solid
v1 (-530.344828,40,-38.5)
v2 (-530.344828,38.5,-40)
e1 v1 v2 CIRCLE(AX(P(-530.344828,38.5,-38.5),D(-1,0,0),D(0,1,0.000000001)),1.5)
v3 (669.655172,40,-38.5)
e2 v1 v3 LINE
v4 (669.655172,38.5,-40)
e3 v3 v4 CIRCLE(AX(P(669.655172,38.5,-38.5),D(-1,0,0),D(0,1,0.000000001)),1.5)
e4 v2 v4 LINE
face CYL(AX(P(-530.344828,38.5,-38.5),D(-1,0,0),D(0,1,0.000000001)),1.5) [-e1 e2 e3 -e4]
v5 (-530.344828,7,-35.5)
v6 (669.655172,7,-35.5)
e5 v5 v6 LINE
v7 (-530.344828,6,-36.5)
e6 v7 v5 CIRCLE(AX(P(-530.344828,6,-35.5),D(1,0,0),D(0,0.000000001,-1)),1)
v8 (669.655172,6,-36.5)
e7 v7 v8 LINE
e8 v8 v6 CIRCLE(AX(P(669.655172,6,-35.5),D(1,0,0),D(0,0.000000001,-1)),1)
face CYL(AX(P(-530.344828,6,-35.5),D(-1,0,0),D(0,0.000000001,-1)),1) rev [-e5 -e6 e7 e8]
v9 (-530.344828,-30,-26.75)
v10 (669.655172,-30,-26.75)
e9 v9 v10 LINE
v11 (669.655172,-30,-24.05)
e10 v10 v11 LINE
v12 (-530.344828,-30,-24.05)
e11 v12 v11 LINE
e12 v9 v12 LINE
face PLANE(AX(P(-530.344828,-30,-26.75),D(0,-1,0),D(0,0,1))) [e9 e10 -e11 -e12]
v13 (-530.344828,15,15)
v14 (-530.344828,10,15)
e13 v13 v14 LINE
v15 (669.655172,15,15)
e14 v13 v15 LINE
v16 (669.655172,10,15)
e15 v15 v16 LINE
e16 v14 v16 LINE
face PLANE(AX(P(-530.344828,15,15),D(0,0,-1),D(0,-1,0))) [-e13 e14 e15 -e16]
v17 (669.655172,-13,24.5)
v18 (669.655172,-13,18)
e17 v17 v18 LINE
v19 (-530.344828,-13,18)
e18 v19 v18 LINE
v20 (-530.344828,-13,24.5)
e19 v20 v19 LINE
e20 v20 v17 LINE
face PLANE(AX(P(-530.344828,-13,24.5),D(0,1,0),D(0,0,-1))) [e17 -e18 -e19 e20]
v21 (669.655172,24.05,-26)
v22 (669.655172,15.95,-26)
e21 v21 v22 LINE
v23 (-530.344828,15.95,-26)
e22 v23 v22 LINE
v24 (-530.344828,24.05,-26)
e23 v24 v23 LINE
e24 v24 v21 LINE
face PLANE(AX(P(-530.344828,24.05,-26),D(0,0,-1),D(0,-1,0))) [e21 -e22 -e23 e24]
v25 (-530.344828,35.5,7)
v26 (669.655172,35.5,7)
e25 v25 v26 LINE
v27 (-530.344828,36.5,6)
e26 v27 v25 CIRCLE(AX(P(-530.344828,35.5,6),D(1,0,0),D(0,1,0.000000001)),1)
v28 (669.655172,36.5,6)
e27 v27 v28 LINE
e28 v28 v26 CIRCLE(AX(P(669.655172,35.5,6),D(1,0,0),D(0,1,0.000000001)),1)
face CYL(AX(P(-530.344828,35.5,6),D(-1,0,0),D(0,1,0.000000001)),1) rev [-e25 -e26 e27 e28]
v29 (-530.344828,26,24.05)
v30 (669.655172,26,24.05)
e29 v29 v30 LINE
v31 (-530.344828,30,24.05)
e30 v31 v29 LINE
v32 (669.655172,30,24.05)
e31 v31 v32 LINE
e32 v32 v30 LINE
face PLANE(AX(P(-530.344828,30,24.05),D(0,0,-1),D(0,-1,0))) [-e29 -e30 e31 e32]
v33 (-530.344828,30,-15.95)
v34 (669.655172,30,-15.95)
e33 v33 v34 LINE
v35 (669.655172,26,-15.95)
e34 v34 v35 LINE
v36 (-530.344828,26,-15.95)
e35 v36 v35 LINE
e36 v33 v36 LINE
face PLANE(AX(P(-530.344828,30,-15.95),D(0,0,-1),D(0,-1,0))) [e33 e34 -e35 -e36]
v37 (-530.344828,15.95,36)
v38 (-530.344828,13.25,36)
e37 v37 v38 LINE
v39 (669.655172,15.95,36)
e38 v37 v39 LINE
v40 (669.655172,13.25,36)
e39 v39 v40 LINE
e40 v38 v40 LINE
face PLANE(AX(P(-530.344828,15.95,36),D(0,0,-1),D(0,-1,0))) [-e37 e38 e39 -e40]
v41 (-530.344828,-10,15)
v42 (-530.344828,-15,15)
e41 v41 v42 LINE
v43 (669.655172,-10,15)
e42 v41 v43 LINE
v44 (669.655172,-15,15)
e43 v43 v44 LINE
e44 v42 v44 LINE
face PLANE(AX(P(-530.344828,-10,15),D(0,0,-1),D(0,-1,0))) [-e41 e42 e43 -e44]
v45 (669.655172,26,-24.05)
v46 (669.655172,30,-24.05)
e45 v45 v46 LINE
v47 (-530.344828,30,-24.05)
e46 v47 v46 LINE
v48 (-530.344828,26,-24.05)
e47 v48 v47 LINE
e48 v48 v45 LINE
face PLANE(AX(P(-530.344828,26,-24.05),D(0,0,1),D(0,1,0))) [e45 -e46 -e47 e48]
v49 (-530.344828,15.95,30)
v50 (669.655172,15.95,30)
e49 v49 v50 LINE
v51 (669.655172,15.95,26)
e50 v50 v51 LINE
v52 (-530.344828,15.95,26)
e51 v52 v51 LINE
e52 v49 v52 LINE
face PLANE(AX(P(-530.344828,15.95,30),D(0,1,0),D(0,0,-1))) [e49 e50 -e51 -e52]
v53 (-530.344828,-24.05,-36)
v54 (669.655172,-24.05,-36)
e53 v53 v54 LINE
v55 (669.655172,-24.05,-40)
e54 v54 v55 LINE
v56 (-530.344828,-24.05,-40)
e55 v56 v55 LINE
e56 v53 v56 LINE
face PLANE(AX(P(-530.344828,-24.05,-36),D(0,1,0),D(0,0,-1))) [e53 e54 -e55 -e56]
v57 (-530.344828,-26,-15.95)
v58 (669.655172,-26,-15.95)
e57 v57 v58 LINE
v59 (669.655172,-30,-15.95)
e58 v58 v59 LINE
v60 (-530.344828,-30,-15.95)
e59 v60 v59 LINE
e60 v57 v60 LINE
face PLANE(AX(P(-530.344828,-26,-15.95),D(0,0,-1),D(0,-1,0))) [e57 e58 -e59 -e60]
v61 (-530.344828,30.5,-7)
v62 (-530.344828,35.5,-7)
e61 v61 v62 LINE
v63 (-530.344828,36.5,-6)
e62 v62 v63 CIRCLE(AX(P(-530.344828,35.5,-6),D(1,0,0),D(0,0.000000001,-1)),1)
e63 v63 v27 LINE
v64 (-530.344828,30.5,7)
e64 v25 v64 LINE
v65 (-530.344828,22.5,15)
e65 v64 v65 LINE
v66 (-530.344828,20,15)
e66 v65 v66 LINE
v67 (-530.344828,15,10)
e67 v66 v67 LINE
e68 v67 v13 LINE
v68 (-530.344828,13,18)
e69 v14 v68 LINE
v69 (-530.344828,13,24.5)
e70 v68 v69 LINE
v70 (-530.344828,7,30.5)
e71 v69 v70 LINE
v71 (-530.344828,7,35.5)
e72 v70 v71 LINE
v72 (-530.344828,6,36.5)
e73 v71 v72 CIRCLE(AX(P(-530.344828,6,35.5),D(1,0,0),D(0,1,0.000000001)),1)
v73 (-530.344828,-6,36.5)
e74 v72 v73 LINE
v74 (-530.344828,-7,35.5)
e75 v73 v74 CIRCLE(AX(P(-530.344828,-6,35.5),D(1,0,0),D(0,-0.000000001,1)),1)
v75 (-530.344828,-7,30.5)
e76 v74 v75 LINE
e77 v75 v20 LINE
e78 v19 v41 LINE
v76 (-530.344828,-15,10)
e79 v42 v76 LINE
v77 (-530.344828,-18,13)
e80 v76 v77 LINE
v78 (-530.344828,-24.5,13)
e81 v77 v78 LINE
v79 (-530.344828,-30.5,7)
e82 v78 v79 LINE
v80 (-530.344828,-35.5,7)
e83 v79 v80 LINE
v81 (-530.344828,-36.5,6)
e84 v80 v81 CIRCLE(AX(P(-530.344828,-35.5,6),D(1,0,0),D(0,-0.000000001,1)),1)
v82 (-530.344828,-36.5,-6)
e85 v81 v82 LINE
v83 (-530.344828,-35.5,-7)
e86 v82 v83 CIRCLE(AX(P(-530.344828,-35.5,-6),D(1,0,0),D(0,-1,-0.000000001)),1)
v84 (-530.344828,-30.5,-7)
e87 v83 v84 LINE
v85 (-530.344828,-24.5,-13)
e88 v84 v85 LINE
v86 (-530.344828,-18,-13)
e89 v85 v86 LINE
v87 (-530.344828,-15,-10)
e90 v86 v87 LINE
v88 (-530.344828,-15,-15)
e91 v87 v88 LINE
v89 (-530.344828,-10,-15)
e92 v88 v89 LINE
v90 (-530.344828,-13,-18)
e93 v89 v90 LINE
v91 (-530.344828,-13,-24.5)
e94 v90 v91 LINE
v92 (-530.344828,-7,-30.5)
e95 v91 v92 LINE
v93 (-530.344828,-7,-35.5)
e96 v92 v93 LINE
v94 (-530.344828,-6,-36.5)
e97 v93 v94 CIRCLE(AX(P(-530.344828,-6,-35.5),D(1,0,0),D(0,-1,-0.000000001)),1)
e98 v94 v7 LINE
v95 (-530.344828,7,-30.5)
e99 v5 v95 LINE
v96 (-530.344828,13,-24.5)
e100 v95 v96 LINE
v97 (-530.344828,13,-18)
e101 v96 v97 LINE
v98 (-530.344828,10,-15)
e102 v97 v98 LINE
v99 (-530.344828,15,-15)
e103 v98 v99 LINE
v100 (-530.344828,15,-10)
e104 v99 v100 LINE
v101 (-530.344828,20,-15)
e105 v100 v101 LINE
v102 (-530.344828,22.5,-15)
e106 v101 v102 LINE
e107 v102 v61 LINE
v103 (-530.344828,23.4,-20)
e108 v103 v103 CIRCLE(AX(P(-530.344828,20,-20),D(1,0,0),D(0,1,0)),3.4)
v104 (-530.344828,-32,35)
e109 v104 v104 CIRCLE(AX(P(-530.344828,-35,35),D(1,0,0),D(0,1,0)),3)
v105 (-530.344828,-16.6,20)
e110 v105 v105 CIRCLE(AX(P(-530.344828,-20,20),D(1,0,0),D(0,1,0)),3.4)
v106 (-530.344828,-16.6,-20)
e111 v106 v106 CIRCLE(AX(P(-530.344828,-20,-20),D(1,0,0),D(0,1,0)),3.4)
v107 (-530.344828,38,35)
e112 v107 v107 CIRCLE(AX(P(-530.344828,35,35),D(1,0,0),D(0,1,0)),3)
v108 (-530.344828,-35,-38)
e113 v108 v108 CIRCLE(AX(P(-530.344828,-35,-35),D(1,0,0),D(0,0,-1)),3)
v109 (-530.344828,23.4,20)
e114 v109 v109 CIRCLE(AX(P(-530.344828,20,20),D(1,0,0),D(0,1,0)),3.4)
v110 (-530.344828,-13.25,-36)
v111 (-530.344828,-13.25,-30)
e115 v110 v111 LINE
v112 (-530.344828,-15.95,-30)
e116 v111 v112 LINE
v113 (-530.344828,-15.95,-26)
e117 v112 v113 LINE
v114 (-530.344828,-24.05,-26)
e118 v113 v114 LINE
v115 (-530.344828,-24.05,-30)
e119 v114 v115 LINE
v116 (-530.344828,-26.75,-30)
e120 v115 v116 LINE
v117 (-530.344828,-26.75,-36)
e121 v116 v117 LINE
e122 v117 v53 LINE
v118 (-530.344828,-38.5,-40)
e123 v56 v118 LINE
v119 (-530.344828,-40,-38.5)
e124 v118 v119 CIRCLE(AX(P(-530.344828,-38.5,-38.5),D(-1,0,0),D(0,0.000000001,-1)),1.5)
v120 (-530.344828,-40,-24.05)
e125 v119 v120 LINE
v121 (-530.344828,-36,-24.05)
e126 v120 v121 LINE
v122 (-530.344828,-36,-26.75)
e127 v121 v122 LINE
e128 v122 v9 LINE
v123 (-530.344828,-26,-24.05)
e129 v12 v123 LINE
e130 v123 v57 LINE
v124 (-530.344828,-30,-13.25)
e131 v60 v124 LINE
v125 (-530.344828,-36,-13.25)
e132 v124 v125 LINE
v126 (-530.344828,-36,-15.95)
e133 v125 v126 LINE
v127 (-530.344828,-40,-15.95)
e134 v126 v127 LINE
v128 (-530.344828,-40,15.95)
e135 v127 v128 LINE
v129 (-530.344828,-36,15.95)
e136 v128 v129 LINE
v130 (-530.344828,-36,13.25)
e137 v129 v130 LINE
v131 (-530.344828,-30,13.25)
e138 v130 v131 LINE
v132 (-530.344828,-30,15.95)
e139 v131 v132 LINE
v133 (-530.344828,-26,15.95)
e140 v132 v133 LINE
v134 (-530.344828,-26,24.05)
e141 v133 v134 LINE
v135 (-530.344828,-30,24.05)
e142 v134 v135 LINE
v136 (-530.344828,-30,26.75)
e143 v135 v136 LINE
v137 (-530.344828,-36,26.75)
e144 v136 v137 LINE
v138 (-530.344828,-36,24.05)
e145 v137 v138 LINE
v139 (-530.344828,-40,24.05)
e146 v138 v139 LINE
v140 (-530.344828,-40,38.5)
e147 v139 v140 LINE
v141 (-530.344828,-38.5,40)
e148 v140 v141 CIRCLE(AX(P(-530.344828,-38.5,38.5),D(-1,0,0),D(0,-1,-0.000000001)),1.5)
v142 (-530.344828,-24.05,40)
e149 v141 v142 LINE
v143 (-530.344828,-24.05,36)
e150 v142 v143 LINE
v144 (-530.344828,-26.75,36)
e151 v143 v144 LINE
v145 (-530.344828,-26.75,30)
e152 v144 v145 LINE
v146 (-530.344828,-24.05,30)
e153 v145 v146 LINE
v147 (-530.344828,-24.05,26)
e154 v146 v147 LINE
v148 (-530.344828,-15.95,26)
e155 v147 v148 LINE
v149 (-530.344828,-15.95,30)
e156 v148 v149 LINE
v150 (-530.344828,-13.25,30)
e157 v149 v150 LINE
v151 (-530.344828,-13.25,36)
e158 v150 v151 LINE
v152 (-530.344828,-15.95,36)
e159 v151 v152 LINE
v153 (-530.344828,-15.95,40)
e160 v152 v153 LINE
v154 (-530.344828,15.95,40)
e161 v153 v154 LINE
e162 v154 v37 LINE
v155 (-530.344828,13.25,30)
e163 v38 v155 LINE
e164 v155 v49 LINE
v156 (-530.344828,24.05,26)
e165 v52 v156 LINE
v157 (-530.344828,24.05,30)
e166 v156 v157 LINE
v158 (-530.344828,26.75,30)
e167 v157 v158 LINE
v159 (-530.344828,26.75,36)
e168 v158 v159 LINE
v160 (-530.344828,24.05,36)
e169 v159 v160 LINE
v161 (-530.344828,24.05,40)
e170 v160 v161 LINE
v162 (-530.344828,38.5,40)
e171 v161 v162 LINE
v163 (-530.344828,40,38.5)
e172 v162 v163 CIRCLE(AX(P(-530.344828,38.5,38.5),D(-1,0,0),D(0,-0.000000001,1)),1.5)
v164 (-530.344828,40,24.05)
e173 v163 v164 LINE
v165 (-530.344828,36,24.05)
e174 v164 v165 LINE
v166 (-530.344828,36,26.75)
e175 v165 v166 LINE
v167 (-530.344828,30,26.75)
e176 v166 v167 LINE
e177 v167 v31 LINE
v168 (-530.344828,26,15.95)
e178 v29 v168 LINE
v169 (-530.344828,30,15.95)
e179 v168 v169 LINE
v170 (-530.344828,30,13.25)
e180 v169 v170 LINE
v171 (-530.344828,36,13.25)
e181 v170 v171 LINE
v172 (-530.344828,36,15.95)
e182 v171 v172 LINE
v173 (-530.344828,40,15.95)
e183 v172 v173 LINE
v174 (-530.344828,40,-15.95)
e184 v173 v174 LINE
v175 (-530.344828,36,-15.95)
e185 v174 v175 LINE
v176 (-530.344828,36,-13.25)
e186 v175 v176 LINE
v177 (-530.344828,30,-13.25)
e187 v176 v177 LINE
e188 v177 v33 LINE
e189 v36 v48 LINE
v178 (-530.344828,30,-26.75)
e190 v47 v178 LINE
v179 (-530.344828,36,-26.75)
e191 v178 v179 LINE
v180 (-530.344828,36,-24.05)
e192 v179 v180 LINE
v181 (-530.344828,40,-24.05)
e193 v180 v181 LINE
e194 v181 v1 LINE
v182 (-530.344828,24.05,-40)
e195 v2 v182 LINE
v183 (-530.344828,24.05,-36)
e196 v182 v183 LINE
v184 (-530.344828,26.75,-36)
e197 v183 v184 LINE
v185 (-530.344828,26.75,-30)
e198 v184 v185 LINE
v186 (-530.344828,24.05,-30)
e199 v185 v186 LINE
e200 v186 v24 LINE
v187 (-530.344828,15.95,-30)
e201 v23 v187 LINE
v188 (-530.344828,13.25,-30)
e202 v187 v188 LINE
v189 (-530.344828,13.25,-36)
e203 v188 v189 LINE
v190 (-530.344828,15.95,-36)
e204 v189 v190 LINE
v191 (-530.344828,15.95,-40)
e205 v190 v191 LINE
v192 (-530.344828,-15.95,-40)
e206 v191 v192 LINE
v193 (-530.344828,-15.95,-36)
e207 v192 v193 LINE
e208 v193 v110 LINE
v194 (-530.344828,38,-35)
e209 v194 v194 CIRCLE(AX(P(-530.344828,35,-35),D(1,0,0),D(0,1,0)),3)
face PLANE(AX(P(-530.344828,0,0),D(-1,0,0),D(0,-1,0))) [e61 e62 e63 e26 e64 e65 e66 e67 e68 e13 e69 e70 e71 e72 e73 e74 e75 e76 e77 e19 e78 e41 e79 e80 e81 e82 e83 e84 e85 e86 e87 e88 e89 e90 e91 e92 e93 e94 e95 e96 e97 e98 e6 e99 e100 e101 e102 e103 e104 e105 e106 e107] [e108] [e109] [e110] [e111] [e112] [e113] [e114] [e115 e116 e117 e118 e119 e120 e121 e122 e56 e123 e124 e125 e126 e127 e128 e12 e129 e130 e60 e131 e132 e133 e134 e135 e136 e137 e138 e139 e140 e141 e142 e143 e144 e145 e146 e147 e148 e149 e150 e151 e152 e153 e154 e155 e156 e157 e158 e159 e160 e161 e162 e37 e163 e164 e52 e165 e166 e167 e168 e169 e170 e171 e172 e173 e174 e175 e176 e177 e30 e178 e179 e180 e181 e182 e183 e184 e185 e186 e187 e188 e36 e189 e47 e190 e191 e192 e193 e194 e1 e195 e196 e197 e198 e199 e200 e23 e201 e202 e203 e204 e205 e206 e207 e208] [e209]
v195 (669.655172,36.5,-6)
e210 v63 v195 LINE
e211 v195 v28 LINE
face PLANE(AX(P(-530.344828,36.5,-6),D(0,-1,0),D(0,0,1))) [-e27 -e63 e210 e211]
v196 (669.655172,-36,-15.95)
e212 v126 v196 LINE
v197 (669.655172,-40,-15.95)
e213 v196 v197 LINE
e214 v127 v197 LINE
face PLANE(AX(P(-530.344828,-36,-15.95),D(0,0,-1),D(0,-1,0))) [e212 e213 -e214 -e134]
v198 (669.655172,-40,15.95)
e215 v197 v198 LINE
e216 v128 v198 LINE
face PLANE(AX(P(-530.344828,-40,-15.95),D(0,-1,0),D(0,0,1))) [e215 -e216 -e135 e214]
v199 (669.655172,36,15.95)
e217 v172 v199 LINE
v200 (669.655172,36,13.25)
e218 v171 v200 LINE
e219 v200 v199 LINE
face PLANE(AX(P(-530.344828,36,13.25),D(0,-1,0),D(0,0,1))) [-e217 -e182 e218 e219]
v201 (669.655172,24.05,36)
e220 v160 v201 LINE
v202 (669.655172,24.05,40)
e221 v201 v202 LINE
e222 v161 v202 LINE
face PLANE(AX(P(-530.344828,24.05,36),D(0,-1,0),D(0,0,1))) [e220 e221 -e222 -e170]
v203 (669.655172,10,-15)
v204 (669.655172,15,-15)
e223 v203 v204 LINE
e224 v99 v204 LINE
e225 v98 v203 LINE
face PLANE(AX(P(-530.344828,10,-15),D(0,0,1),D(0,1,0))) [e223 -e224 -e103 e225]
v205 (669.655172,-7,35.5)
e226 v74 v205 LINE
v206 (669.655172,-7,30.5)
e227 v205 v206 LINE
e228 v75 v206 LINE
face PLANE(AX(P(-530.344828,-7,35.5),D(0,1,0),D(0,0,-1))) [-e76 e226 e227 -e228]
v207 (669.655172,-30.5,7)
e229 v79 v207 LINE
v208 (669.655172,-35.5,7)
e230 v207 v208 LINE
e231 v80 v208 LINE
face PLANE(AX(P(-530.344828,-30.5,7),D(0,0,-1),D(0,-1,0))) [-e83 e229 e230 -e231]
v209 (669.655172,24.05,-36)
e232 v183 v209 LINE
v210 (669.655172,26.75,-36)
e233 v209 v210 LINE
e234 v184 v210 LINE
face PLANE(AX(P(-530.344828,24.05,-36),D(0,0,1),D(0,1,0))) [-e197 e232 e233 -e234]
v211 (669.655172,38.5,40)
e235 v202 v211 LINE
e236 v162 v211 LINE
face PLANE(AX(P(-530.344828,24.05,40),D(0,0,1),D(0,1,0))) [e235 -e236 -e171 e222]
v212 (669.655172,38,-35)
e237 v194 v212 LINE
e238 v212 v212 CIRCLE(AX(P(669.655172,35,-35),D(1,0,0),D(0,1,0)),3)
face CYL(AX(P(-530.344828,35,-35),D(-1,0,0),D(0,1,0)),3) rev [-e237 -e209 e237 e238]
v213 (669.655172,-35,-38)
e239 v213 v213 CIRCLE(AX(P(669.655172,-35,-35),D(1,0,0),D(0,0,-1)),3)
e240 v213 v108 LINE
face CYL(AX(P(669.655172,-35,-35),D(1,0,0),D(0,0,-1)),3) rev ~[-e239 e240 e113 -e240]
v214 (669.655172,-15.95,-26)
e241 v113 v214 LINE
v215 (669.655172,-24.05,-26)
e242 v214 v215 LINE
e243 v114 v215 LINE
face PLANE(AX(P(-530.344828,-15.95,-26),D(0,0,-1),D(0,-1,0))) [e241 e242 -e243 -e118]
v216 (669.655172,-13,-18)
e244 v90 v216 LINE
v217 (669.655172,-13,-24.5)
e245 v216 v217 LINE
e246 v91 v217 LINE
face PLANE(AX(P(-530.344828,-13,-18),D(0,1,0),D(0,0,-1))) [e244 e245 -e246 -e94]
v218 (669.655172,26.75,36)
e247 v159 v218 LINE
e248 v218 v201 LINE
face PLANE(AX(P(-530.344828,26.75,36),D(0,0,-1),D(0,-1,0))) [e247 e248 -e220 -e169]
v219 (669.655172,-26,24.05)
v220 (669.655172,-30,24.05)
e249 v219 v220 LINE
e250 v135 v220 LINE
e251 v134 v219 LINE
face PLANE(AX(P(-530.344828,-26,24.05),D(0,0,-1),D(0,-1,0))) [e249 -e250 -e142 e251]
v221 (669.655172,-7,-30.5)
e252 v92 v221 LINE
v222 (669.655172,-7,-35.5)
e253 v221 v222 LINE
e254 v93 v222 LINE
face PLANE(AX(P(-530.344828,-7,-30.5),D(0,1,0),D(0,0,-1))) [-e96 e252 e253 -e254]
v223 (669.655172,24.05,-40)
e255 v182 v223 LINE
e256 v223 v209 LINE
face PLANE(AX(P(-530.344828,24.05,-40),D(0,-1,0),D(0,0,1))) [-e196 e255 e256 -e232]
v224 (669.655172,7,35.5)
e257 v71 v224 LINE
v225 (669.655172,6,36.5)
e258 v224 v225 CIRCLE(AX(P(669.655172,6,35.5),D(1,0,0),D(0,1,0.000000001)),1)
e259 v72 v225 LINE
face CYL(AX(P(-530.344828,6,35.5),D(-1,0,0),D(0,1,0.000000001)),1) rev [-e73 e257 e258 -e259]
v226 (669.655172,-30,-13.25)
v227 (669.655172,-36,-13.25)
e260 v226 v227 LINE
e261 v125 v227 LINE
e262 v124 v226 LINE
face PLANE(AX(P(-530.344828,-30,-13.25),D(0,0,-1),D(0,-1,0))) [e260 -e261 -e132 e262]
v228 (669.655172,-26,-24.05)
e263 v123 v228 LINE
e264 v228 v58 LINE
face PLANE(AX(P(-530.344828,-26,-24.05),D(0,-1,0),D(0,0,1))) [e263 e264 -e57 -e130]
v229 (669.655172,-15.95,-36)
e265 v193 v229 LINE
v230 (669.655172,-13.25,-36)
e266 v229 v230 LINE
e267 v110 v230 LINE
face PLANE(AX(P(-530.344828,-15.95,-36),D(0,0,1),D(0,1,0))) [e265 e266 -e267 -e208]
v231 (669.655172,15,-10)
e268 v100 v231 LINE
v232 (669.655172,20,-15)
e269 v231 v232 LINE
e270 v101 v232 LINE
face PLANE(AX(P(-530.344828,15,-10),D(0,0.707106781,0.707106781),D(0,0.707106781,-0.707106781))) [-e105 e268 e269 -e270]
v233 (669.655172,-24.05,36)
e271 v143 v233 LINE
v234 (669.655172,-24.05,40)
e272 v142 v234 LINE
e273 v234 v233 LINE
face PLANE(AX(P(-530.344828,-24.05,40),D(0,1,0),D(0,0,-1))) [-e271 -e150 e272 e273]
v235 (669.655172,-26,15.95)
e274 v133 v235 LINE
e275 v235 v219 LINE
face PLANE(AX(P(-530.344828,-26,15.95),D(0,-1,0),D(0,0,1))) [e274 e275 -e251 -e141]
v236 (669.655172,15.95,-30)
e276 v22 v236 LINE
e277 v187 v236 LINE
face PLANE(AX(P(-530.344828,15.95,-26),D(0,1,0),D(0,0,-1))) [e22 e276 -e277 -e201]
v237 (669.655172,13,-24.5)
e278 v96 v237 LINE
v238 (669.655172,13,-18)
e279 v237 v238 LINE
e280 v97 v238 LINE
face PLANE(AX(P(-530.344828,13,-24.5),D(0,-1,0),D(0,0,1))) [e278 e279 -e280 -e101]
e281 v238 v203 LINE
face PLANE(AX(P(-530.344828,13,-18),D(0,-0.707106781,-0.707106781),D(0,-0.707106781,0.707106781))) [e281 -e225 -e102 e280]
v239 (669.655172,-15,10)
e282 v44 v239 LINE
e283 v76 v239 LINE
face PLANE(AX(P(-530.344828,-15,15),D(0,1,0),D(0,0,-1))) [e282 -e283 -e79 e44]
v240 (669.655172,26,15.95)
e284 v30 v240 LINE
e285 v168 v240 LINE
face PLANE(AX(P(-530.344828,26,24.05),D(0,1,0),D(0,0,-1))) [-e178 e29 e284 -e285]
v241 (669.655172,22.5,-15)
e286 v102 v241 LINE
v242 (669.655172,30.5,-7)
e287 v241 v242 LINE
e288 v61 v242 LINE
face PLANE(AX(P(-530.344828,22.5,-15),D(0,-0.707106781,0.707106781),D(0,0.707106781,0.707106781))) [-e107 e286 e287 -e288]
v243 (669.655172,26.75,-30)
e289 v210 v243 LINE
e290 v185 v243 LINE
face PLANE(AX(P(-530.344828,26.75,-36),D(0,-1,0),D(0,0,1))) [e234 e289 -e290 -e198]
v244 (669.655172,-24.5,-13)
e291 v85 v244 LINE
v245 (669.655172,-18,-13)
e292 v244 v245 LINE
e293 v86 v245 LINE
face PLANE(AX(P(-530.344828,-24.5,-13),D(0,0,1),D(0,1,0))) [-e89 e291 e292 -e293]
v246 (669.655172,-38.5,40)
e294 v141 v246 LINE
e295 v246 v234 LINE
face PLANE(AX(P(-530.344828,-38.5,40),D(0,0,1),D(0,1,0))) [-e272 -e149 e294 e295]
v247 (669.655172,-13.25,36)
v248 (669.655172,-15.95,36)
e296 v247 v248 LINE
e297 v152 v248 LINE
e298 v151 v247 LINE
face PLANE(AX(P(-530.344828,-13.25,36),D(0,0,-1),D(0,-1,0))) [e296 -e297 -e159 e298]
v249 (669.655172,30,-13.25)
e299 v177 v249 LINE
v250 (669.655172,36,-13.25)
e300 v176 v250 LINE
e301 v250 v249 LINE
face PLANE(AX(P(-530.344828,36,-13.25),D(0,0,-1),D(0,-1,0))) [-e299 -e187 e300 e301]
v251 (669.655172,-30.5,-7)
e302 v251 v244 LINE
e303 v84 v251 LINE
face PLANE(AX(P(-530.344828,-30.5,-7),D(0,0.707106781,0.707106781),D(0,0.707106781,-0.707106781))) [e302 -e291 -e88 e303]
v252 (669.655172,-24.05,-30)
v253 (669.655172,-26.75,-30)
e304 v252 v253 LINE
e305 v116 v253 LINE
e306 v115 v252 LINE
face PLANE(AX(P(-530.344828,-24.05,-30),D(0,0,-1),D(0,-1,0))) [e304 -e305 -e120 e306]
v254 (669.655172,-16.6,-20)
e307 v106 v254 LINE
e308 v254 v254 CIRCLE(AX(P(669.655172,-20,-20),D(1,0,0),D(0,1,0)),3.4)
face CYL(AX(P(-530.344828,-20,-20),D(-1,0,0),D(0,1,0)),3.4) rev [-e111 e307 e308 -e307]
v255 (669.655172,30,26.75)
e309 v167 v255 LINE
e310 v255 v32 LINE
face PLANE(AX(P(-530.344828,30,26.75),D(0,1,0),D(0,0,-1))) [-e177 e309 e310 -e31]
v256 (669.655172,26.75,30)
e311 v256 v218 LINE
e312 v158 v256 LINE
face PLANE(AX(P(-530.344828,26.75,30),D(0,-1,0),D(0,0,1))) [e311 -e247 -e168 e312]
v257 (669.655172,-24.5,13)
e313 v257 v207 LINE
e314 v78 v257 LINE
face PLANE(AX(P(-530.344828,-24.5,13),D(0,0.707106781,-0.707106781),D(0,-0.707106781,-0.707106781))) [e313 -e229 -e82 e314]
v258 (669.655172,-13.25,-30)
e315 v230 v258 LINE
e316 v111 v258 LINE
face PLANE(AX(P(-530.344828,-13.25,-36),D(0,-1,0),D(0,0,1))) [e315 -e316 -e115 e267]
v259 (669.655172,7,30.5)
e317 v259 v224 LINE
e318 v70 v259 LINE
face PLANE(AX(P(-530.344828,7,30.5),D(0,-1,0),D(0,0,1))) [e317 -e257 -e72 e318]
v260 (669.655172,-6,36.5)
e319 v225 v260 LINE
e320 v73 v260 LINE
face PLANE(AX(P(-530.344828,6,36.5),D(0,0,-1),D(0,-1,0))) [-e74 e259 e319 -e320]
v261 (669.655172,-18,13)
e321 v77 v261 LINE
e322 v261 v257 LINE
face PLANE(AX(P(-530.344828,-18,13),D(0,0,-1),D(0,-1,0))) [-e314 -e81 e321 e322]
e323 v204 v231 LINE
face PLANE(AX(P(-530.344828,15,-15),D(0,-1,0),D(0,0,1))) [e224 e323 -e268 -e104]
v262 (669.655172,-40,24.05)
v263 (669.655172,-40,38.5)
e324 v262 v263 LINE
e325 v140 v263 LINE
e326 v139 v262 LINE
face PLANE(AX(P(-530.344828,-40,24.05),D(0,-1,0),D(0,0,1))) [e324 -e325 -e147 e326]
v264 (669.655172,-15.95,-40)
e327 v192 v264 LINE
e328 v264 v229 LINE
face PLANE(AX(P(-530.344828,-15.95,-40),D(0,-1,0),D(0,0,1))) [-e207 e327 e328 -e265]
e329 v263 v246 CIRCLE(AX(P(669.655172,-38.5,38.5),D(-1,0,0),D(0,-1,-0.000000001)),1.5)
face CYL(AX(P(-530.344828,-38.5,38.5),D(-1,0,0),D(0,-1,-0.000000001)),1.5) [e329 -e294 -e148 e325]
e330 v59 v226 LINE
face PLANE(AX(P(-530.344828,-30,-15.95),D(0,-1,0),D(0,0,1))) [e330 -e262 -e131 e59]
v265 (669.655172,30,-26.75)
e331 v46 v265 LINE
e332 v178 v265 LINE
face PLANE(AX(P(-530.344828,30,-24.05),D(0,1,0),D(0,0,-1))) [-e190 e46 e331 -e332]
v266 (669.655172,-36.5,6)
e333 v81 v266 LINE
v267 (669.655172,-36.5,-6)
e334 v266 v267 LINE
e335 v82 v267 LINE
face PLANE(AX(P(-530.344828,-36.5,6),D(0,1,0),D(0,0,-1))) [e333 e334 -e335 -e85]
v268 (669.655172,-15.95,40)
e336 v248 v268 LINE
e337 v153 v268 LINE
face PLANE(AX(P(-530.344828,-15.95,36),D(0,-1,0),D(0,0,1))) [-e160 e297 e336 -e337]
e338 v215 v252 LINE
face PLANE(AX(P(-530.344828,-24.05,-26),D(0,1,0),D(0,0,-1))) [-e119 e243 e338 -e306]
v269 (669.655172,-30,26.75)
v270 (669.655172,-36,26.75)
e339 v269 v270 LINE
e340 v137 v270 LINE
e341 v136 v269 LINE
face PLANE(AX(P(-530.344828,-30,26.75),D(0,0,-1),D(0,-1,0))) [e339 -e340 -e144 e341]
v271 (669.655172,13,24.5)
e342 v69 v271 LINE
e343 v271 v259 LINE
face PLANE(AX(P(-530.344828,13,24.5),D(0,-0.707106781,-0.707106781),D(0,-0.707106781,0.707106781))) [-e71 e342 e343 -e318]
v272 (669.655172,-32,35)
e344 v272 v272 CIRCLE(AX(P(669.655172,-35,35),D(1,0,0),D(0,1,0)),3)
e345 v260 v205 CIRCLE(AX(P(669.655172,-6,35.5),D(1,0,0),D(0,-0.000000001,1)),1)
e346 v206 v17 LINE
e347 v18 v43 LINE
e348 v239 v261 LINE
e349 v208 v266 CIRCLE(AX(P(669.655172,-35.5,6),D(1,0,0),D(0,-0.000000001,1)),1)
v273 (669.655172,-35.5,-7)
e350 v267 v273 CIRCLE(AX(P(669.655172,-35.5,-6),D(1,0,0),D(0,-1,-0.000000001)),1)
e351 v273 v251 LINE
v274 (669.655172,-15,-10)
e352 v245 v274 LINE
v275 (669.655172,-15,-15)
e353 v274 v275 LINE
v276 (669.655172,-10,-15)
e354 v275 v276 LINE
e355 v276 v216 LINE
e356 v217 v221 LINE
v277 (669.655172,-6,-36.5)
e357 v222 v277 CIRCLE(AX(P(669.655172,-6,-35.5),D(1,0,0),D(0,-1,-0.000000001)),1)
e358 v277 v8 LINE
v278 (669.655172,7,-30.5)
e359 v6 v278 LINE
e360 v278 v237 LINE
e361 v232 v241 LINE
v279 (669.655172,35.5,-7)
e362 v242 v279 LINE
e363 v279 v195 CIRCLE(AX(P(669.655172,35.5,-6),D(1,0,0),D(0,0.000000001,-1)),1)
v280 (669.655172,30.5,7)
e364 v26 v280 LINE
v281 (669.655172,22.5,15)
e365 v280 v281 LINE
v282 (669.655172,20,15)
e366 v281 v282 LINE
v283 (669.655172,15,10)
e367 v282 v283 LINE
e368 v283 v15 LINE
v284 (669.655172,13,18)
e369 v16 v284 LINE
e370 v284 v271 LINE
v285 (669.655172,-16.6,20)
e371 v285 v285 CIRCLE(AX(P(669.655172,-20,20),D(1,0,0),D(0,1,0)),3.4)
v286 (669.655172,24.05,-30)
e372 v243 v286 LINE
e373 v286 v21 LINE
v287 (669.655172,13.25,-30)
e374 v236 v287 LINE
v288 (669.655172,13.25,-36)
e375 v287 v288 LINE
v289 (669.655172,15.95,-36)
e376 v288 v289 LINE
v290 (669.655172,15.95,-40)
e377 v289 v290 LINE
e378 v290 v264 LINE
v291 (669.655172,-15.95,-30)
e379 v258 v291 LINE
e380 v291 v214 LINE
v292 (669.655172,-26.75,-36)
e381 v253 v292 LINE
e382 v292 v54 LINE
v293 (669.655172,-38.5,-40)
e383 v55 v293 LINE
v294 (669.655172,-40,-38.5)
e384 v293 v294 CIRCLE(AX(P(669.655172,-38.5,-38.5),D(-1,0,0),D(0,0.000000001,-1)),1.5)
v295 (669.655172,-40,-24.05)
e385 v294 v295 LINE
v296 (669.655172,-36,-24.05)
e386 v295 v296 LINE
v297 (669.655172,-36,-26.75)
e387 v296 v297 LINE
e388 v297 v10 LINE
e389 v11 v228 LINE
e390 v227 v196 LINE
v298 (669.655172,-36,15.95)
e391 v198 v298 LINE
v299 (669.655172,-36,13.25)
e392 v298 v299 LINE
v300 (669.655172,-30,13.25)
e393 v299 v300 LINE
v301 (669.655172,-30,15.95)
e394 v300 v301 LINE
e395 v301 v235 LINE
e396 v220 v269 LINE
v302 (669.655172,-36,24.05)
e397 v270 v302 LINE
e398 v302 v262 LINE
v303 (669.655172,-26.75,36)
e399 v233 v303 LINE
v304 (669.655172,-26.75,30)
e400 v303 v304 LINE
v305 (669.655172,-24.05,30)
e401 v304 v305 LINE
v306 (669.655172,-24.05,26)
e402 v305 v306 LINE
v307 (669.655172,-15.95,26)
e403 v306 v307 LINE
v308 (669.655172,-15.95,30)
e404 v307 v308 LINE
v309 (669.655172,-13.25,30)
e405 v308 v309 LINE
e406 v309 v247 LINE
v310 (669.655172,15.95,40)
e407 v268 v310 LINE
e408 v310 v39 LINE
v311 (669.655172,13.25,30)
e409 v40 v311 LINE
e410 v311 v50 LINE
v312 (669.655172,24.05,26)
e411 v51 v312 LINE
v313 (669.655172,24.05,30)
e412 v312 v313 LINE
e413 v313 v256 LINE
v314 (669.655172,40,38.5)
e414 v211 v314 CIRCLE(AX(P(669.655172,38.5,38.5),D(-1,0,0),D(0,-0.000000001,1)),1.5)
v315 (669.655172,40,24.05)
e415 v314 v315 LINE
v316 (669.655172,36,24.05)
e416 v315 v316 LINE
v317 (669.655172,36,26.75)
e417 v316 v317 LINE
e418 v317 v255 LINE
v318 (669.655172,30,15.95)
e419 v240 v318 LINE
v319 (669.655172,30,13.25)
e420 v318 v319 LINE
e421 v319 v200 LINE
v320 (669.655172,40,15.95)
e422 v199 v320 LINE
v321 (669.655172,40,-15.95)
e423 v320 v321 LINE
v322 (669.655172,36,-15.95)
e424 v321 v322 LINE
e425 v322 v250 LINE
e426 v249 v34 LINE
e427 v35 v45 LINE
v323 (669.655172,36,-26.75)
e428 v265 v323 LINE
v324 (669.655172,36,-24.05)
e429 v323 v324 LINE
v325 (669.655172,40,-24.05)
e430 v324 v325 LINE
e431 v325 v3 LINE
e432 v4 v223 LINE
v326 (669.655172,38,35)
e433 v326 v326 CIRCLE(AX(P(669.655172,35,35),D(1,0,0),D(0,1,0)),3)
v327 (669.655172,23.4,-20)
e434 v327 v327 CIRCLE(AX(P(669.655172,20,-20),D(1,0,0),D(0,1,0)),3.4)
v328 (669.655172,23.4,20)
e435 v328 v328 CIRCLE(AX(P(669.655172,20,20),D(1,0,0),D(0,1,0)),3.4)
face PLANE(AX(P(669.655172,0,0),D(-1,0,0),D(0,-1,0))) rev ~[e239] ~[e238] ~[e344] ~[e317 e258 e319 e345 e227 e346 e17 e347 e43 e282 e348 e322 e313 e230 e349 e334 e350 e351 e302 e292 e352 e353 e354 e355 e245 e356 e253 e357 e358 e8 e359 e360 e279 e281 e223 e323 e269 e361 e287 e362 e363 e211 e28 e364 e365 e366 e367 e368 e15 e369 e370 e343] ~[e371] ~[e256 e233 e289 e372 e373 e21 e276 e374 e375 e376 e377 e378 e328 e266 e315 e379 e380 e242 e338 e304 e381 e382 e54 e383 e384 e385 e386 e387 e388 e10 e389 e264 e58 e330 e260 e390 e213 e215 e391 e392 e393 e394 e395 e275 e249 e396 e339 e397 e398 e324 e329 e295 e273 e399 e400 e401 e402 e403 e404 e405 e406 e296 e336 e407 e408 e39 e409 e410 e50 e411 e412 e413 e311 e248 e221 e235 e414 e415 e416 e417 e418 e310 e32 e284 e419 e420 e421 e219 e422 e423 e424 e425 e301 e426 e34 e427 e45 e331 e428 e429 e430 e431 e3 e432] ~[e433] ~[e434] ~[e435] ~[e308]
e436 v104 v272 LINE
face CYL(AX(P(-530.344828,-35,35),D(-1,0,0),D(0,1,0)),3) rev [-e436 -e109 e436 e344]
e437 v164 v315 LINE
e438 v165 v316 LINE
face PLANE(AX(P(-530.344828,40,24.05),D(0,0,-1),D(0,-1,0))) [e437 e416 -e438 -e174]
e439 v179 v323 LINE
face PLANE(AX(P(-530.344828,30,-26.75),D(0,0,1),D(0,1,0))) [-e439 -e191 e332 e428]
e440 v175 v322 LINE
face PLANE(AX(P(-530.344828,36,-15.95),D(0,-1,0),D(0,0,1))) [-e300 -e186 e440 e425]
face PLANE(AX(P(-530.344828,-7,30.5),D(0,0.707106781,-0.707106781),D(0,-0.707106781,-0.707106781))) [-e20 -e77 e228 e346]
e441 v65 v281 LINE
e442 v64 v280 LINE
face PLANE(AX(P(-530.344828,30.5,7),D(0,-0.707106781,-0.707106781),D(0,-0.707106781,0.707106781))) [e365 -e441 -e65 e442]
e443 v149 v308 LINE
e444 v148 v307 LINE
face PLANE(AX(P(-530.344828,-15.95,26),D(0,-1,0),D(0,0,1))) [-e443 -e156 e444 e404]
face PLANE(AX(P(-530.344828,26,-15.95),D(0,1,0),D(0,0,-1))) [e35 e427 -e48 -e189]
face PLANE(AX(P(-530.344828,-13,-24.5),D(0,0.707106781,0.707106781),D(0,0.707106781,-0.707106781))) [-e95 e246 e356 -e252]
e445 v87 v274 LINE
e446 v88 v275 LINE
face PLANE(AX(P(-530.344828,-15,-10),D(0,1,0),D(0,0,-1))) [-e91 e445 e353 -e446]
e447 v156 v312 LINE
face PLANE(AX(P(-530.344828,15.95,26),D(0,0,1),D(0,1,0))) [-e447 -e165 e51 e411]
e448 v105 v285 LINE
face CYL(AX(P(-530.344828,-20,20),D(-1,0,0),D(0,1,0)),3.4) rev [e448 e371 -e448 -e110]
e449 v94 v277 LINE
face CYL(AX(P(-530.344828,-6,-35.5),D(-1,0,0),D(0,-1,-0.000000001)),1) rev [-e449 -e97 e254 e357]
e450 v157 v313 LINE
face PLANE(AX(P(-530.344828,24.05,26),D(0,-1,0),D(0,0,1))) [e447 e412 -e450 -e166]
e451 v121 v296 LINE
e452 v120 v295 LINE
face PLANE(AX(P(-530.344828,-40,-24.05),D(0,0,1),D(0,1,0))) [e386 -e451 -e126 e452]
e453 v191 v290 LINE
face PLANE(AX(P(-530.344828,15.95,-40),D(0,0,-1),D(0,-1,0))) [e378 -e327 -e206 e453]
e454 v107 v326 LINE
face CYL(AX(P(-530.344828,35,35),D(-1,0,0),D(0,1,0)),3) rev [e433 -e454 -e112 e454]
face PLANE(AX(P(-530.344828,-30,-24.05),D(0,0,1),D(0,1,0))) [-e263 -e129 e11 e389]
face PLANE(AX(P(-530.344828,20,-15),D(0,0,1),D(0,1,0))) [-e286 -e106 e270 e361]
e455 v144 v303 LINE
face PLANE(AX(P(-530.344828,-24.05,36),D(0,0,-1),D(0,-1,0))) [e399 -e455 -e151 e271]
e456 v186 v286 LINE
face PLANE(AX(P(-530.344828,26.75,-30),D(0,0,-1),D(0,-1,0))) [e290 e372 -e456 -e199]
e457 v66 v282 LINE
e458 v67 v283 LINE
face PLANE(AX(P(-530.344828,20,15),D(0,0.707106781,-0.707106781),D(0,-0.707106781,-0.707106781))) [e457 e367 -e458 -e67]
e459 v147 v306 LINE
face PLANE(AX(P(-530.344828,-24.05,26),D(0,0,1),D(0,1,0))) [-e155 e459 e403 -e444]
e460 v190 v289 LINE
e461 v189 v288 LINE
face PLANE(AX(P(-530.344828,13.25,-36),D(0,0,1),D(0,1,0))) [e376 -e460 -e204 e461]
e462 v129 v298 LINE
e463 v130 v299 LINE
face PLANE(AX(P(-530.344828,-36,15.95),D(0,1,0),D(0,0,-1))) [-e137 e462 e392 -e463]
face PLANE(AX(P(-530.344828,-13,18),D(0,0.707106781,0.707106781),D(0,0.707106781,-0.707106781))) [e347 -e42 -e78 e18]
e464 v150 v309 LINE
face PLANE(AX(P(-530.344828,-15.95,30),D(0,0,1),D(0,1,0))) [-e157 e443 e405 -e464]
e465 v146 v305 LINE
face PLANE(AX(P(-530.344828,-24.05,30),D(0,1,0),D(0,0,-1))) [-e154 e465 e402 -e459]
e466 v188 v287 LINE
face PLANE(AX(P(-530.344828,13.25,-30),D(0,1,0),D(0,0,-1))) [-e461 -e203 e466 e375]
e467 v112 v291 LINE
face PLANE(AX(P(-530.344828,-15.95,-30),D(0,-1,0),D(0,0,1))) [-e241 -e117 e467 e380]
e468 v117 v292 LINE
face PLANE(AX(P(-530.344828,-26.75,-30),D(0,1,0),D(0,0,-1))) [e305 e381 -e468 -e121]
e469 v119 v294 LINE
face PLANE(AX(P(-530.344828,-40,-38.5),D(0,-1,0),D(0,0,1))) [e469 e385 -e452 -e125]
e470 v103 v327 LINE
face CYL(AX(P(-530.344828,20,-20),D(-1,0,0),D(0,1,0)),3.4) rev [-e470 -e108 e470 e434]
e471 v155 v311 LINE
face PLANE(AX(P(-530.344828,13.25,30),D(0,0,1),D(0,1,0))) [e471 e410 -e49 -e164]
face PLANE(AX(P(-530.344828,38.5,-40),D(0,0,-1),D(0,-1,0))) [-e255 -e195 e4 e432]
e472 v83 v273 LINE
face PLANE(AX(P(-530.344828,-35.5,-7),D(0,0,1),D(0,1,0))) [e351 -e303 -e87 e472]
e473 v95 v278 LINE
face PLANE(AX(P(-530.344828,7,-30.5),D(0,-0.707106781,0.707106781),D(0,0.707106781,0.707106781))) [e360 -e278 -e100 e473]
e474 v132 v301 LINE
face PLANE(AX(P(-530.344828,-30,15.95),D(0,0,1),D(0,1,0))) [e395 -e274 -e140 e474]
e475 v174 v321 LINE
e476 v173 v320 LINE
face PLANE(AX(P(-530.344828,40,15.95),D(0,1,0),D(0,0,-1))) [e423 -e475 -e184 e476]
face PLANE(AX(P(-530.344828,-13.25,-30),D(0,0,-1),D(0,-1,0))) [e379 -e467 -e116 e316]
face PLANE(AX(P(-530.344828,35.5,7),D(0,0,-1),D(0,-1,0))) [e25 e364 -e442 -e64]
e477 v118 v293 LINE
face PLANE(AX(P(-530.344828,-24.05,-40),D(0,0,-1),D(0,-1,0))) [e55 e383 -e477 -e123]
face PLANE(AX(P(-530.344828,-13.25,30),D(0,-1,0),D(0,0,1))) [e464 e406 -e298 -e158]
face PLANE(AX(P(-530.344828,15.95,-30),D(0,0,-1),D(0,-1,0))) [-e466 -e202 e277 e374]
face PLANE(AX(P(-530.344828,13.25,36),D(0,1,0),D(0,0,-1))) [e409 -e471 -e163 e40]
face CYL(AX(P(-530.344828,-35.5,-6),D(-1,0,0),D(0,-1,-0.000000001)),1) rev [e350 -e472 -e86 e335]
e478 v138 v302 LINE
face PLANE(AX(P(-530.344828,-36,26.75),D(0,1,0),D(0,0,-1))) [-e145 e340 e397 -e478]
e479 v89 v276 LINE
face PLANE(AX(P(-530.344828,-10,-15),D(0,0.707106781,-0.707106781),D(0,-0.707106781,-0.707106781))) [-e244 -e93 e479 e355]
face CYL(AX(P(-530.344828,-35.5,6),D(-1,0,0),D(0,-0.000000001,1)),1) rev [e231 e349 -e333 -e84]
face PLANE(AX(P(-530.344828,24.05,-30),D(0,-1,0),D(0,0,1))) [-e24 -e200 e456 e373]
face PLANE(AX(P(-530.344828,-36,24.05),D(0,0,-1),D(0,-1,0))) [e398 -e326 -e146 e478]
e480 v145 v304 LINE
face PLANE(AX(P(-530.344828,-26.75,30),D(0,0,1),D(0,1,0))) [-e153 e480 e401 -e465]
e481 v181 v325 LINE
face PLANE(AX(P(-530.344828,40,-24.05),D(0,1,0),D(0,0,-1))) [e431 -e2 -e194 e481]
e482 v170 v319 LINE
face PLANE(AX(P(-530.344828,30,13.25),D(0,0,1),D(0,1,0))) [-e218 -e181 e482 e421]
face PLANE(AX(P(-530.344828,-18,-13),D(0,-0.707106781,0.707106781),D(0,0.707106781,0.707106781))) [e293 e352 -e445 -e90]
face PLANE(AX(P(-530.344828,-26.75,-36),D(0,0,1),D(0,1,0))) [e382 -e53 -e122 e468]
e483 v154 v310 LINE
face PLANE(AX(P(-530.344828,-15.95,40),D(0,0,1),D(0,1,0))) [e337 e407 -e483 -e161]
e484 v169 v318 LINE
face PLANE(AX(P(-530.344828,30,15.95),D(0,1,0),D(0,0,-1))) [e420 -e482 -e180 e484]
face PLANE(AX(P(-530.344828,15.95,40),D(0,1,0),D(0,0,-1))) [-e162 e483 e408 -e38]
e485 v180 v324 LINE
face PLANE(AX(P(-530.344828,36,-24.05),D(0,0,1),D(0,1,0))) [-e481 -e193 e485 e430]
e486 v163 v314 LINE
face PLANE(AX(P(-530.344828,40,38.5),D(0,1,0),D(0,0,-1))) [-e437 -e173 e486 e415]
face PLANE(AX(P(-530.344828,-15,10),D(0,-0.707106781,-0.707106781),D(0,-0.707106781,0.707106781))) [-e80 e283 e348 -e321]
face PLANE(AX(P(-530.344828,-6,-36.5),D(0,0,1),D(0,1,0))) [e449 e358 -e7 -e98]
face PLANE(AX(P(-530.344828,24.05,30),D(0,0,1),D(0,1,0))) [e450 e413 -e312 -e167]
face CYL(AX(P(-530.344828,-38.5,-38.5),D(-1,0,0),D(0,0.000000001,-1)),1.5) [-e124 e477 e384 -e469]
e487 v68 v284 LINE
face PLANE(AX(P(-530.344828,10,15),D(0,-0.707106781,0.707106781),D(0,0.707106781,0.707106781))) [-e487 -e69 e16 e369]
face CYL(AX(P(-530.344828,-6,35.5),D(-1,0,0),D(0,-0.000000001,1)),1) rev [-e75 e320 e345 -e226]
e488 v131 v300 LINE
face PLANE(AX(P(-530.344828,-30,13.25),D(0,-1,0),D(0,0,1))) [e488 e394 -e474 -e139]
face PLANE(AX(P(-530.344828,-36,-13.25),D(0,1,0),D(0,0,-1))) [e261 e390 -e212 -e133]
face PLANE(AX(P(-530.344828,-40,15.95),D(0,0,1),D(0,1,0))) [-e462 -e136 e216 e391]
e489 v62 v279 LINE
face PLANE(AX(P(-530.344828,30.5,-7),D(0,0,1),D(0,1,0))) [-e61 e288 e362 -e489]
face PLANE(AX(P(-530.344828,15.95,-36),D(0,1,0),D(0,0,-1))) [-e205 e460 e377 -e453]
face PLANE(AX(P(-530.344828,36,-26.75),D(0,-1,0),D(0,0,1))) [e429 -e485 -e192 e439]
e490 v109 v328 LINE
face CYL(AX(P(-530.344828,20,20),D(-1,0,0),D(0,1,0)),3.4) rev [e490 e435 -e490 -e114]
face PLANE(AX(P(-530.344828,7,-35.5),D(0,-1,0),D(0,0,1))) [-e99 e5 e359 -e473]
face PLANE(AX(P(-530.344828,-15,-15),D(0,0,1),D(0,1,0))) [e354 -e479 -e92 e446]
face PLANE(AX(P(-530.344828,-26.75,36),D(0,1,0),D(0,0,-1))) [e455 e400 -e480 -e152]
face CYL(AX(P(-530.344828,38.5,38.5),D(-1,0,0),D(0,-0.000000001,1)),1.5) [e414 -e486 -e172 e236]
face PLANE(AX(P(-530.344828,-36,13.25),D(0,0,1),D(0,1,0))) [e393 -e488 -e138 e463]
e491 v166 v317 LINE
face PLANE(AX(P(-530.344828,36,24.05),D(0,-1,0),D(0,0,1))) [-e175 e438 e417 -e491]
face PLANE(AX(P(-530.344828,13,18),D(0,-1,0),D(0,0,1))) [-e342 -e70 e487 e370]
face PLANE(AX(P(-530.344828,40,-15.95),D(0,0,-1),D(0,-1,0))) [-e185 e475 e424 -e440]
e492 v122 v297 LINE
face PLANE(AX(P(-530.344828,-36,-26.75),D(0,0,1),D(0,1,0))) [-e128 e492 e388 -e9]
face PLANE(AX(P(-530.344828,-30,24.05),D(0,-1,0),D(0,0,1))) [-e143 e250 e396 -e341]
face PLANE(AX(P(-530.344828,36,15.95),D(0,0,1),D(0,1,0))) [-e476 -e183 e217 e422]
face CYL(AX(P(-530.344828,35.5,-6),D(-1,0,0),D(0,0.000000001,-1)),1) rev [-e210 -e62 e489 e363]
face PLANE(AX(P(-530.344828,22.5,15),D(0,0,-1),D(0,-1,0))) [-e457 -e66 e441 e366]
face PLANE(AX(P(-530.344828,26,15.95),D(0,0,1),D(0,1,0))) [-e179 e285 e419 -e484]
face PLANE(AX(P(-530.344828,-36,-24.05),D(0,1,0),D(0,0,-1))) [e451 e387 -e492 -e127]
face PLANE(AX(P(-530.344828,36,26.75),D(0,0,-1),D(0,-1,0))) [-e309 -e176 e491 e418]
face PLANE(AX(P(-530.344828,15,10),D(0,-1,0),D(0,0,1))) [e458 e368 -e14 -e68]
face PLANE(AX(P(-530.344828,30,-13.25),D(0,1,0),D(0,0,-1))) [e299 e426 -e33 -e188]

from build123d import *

# Parameters (mm, degrees)
SKETCH1_R                                 = 3.4
SKETCH1_R_2                               = 3
ALUMINIUM_PROFILE_80_X_80G_X_R1_5_1_DEPTH = 1200
SKETCH10_R                                = 3
CUT_EXTRUDE1_DEPTH                        = 1202.332593414


with BuildPart() as part:
    # Sketch1 → Aluminium profile 80 X 80G X R1.5(1) (new body)
    with BuildSketch(Plane.YZ.offset(-530.344827586)):
        with BuildLine():
            Line((-24.05, 40), (-24.05, 36))
            Line((-24.05, 36), (-26.75, 36))
            Line((-26.75, 36), (-26.75, 30))
            Line((-26.75, 30), (-24.05, 30))
            Line((-24.05, 30), (-24.05, 26))
            Line((-24.05, 26), (-15.95, 26))
            Line((-15.95, 26), (-15.95, 30))
            Line((-15.95, 30), (-13.25, 30))
            Line((-13.25, 30), (-13.25, 36))
            Line((-13.25, 36), (-15.95, 36))
            Line((-15.95, 36), (-15.95, 40))
            Line((-15.95, 40), (15.95, 40))
            Line((15.95, 40), (15.95, 36))
            Line((15.95, 36), (13.25, 36))
            Line((13.25, 36), (13.25, 30))
            Line((13.25, 30), (15.95, 30))
            Line((15.95, 30), (15.95, 26))
            Line((15.95, 26), (24.05, 26))
            Line((24.05, 26), (24.05, 30))
            Line((24.05, 30), (26.75, 30))
            Line((26.75, 30), (26.75, 36))
            Line((26.75, 36), (24.05, 36))
            Line((24.05, 36), (24.05, 40))
            Line((24.05, 40), (38.5, 40))
            ThreePointArc((38.5, 40), (39.560660172, 39.560660172), (40, 38.5))
            Line((40, 38.5), (40, 24.05))
            Line((40, 24.05), (36, 24.05))
            Line((36, 24.05), (36, 26.75))
            Line((36, 26.75), (30, 26.75))
            Line((30, 26.75), (30, 24.05))
            Line((30, 24.05), (26, 24.05))
            Line((26, 24.05), (26, 15.95))
            Line((26, 15.95), (30, 15.95))
            Line((30, 15.95), (30, 13.25))
            Line((30, 13.25), (36, 13.25))
            Line((36, 13.25), (36, 15.95))
            Line((36, 15.95), (40, 15.95))
            Line((40, 15.95), (40, -15.95))
            Line((40, -15.95), (36, -15.95))
            Line((36, -15.95), (36, -13.25))
            Line((36, -13.25), (30, -13.25))
            Line((30, -13.25), (30, -15.95))
            Line((30, -15.95), (26, -15.95))
            Line((26, -15.95), (26, -24.05))
            Line((26, -24.05), (30, -24.05))
            Line((30, -24.05), (30, -26.75))
            Line((30, -26.75), (36, -26.75))
            Line((36, -26.75), (36, -24.05))
            Line((36, -24.05), (40, -24.05))
            Line((40, -24.05), (40, -38.5))
            ThreePointArc((40, -38.5), (39.560660172, -39.560660172), (38.5, -40))
            Line((38.5, -40), (24.05, -40))
            Line((24.05, -40), (24.05, -36))
            Line((24.05, -36), (26.75, -36))
            Line((26.75, -36), (26.75, -30))
            Line((26.75, -30), (24.05, -30))
            Line((24.05, -30), (24.05, -26))
            Line((24.05, -26), (15.95, -26))
            Line((15.95, -26), (15.95, -30))
            Line((15.95, -30), (13.25, -30))
            Line((13.25, -30), (13.25, -36))
            Line((13.25, -36), (15.95, -36))
            Line((15.95, -36), (15.95, -40))
            Line((15.95, -40), (-15.95, -40))
            Line((-15.95, -40), (-15.95, -36))
            Line((-15.95, -36), (-13.25, -36))
            Line((-13.25, -36), (-13.25, -30))
            Line((-13.25, -30), (-15.95, -30))
            Line((-15.95, -30), (-15.95, -26))
            Line((-15.95, -26), (-24.05, -26))
            Line((-24.05, -26), (-24.05, -30))
            Line((-24.05, -30), (-26.75, -30))
            Line((-26.75, -30), (-26.75, -36))
            Line((-26.75, -36), (-24.05, -36))
            Line((-24.05, -36), (-24.05, -40))
            Line((-24.05, -40), (-38.5, -40))
            ThreePointArc((-38.5, -40), (-39.560660172, -39.560660172), (-40, -38.5))
            Line((-40, -38.5), (-40, -24.05))
            Line((-40, -24.05), (-36, -24.05))
            Line((-36, -24.05), (-36, -26.75))
            Line((-36, -26.75), (-30, -26.75))
            Line((-30, -26.75), (-30, -24.05))
            Line((-30, -24.05), (-26, -24.05))
            Line((-26, -24.05), (-26, -15.95))
            Line((-26, -15.95), (-30, -15.95))
            Line((-30, -15.95), (-30, -13.25))
            Line((-30, -13.25), (-36, -13.25))
            Line((-36, -13.25), (-36, -15.95))
            Line((-36, -15.95), (-40, -15.95))
            Line((-40, -15.95), (-40, 15.95))
            Line((-40, 15.95), (-36, 15.95))
            Line((-36, 15.95), (-36, 13.25))
            Line((-36, 13.25), (-30, 13.25))
            Line((-30, 13.25), (-30, 15.95))
            Line((-30, 15.95), (-26, 15.95))
            Line((-26, 15.95), (-26, 24.05))
            Line((-26, 24.05), (-30, 24.05))
            Line((-30, 24.05), (-30, 26.75))
            Line((-30, 26.75), (-36, 26.75))
            Line((-36, 26.75), (-36, 24.05))
            Line((-36, 24.05), (-40, 24.05))
            Line((-40, 24.05), (-40, 38.5))
            ThreePointArc((-40, 38.5), (-39.560660172, 39.560660172), (-38.5, 40))
            Line((-38.5, 40), (-24.05, 40))
        make_face()
        with Locations((-20, 20)):
            Circle(SKETCH1_R, mode=Mode.SUBTRACT)
        with Locations((20, 20)):
            Circle(SKETCH1_R, mode=Mode.SUBTRACT)
        with Locations((20, -20)):
            Circle(SKETCH1_R, mode=Mode.SUBTRACT)
        with Locations((-20, -20)):
            Circle(SKETCH1_R, mode=Mode.SUBTRACT)
        with Locations((-35, 35)):
            Circle(SKETCH1_R_2, mode=Mode.SUBTRACT)
        with Locations((35, 35)):
            Circle(SKETCH1_R_2, mode=Mode.SUBTRACT)
        with Locations((35, -35)):
            Circle(SKETCH1_R_2, mode=Mode.SUBTRACT)
        with BuildLine():
            Line((-13, 18), (-10, 15))
            Line((-10, 15), (-15, 15))
            Line((-15, 15), (-15, 10))
            Line((-15, 10), (-18, 13))
            Line((-18, 13), (-24.5, 13))
            Line((-24.5, 13), (-30.5, 7))
            Line((-30.5, 7), (-35.5, 7))
            ThreePointArc((-35.5, 7), (-36.207106781, 6.707106781), (-36.5, 6))
            Line((-36.5, 6), (-36.5, -6))
            ThreePointArc((-36.5, -6), (-36.207106781, -6.707106781), (-35.5, -7))
            Line((-35.5, -7), (-30.5, -7))
            Line((-30.5, -7), (-24.5, -13))
            Line((-24.5, -13), (-18, -13))
            Line((-18, -13), (-15, -10))
            Line((-15, -10), (-15, -15))
            Line((-15, -15), (-10, -15))
            Line((-10, -15), (-13, -18))
            Line((-13, -18), (-13, -24.5))
            Line((-13, -24.5), (-7, -30.5))
            Line((-7, -30.5), (-7, -35.5))
            ThreePointArc((-7, -35.5), (-6.707106781, -36.207106781), (-6, -36.5))
            Line((-6, -36.5), (6, -36.5))
            ThreePointArc((6, -36.5), (6.707106781, -36.207106781), (7, -35.5))
            Line((7, -35.5), (7, -30.5))
            Line((7, -30.5), (13, -24.5))
            Line((13, -24.5), (13, -18))
            Line((13, -18), (10, -15))
            Line((10, -15), (15, -15))
            Line((15, -15), (15, -10))
            Line((15, -10), (20, -15))
            Line((20, -15), (22.5, -15))
            Line((22.5, -15), (30.5, -7))
            Line((30.5, -7), (35.5, -7))
            ThreePointArc((35.5, -7), (36.207106781, -6.707106781), (36.5, -6))
            Line((36.5, -6), (36.5, 6))
            ThreePointArc((36.5, 6), (36.207106781, 6.707106781), (35.5, 7))
            Line((35.5, 7), (30.5, 7))
            Line((30.5, 7), (22.5, 15))
            Line((22.5, 15), (20, 15))
            Line((20, 15), (15, 10))
            Line((15, 10), (15, 15))
            Line((15, 15), (10, 15))
            Line((10, 15), (13, 18))
            Line((13, 18), (13, 24.5))
            Line((13, 24.5), (7, 30.5))
            Line((7, 30.5), (7, 35.5))
            ThreePointArc((7, 35.5), (6.707106781, 36.207106781), (6, 36.5))
            Line((6, 36.5), (-6, 36.5))
            ThreePointArc((-6, 36.5), (-6.707106781, 36.207106781), (-7, 35.5))
            Line((-7, 35.5), (-7, 30.5))
            Line((-7, 30.5), (-13, 24.5))
            Line((-13, 24.5), (-13, 18))
        make_face(mode=Mode.SUBTRACT)
    extrude(amount=ALUMINIUM_PROFILE_80_X_80G_X_R1_5_1_DEPTH)

    # Sketch10 → Cut-Extrude1 (cut, through all)
    with BuildSketch(Plane(origin=(669.655172414, 0, 0), x_dir=(0, 0, -1), z_dir=(1, 0, 0))):
        with Locations((35, -35)):
            Circle(SKETCH10_R)
    extrude(amount=-CUT_EXTRUDE1_DEPTH, mode=Mode.SUBTRACT)


solid = part.part
